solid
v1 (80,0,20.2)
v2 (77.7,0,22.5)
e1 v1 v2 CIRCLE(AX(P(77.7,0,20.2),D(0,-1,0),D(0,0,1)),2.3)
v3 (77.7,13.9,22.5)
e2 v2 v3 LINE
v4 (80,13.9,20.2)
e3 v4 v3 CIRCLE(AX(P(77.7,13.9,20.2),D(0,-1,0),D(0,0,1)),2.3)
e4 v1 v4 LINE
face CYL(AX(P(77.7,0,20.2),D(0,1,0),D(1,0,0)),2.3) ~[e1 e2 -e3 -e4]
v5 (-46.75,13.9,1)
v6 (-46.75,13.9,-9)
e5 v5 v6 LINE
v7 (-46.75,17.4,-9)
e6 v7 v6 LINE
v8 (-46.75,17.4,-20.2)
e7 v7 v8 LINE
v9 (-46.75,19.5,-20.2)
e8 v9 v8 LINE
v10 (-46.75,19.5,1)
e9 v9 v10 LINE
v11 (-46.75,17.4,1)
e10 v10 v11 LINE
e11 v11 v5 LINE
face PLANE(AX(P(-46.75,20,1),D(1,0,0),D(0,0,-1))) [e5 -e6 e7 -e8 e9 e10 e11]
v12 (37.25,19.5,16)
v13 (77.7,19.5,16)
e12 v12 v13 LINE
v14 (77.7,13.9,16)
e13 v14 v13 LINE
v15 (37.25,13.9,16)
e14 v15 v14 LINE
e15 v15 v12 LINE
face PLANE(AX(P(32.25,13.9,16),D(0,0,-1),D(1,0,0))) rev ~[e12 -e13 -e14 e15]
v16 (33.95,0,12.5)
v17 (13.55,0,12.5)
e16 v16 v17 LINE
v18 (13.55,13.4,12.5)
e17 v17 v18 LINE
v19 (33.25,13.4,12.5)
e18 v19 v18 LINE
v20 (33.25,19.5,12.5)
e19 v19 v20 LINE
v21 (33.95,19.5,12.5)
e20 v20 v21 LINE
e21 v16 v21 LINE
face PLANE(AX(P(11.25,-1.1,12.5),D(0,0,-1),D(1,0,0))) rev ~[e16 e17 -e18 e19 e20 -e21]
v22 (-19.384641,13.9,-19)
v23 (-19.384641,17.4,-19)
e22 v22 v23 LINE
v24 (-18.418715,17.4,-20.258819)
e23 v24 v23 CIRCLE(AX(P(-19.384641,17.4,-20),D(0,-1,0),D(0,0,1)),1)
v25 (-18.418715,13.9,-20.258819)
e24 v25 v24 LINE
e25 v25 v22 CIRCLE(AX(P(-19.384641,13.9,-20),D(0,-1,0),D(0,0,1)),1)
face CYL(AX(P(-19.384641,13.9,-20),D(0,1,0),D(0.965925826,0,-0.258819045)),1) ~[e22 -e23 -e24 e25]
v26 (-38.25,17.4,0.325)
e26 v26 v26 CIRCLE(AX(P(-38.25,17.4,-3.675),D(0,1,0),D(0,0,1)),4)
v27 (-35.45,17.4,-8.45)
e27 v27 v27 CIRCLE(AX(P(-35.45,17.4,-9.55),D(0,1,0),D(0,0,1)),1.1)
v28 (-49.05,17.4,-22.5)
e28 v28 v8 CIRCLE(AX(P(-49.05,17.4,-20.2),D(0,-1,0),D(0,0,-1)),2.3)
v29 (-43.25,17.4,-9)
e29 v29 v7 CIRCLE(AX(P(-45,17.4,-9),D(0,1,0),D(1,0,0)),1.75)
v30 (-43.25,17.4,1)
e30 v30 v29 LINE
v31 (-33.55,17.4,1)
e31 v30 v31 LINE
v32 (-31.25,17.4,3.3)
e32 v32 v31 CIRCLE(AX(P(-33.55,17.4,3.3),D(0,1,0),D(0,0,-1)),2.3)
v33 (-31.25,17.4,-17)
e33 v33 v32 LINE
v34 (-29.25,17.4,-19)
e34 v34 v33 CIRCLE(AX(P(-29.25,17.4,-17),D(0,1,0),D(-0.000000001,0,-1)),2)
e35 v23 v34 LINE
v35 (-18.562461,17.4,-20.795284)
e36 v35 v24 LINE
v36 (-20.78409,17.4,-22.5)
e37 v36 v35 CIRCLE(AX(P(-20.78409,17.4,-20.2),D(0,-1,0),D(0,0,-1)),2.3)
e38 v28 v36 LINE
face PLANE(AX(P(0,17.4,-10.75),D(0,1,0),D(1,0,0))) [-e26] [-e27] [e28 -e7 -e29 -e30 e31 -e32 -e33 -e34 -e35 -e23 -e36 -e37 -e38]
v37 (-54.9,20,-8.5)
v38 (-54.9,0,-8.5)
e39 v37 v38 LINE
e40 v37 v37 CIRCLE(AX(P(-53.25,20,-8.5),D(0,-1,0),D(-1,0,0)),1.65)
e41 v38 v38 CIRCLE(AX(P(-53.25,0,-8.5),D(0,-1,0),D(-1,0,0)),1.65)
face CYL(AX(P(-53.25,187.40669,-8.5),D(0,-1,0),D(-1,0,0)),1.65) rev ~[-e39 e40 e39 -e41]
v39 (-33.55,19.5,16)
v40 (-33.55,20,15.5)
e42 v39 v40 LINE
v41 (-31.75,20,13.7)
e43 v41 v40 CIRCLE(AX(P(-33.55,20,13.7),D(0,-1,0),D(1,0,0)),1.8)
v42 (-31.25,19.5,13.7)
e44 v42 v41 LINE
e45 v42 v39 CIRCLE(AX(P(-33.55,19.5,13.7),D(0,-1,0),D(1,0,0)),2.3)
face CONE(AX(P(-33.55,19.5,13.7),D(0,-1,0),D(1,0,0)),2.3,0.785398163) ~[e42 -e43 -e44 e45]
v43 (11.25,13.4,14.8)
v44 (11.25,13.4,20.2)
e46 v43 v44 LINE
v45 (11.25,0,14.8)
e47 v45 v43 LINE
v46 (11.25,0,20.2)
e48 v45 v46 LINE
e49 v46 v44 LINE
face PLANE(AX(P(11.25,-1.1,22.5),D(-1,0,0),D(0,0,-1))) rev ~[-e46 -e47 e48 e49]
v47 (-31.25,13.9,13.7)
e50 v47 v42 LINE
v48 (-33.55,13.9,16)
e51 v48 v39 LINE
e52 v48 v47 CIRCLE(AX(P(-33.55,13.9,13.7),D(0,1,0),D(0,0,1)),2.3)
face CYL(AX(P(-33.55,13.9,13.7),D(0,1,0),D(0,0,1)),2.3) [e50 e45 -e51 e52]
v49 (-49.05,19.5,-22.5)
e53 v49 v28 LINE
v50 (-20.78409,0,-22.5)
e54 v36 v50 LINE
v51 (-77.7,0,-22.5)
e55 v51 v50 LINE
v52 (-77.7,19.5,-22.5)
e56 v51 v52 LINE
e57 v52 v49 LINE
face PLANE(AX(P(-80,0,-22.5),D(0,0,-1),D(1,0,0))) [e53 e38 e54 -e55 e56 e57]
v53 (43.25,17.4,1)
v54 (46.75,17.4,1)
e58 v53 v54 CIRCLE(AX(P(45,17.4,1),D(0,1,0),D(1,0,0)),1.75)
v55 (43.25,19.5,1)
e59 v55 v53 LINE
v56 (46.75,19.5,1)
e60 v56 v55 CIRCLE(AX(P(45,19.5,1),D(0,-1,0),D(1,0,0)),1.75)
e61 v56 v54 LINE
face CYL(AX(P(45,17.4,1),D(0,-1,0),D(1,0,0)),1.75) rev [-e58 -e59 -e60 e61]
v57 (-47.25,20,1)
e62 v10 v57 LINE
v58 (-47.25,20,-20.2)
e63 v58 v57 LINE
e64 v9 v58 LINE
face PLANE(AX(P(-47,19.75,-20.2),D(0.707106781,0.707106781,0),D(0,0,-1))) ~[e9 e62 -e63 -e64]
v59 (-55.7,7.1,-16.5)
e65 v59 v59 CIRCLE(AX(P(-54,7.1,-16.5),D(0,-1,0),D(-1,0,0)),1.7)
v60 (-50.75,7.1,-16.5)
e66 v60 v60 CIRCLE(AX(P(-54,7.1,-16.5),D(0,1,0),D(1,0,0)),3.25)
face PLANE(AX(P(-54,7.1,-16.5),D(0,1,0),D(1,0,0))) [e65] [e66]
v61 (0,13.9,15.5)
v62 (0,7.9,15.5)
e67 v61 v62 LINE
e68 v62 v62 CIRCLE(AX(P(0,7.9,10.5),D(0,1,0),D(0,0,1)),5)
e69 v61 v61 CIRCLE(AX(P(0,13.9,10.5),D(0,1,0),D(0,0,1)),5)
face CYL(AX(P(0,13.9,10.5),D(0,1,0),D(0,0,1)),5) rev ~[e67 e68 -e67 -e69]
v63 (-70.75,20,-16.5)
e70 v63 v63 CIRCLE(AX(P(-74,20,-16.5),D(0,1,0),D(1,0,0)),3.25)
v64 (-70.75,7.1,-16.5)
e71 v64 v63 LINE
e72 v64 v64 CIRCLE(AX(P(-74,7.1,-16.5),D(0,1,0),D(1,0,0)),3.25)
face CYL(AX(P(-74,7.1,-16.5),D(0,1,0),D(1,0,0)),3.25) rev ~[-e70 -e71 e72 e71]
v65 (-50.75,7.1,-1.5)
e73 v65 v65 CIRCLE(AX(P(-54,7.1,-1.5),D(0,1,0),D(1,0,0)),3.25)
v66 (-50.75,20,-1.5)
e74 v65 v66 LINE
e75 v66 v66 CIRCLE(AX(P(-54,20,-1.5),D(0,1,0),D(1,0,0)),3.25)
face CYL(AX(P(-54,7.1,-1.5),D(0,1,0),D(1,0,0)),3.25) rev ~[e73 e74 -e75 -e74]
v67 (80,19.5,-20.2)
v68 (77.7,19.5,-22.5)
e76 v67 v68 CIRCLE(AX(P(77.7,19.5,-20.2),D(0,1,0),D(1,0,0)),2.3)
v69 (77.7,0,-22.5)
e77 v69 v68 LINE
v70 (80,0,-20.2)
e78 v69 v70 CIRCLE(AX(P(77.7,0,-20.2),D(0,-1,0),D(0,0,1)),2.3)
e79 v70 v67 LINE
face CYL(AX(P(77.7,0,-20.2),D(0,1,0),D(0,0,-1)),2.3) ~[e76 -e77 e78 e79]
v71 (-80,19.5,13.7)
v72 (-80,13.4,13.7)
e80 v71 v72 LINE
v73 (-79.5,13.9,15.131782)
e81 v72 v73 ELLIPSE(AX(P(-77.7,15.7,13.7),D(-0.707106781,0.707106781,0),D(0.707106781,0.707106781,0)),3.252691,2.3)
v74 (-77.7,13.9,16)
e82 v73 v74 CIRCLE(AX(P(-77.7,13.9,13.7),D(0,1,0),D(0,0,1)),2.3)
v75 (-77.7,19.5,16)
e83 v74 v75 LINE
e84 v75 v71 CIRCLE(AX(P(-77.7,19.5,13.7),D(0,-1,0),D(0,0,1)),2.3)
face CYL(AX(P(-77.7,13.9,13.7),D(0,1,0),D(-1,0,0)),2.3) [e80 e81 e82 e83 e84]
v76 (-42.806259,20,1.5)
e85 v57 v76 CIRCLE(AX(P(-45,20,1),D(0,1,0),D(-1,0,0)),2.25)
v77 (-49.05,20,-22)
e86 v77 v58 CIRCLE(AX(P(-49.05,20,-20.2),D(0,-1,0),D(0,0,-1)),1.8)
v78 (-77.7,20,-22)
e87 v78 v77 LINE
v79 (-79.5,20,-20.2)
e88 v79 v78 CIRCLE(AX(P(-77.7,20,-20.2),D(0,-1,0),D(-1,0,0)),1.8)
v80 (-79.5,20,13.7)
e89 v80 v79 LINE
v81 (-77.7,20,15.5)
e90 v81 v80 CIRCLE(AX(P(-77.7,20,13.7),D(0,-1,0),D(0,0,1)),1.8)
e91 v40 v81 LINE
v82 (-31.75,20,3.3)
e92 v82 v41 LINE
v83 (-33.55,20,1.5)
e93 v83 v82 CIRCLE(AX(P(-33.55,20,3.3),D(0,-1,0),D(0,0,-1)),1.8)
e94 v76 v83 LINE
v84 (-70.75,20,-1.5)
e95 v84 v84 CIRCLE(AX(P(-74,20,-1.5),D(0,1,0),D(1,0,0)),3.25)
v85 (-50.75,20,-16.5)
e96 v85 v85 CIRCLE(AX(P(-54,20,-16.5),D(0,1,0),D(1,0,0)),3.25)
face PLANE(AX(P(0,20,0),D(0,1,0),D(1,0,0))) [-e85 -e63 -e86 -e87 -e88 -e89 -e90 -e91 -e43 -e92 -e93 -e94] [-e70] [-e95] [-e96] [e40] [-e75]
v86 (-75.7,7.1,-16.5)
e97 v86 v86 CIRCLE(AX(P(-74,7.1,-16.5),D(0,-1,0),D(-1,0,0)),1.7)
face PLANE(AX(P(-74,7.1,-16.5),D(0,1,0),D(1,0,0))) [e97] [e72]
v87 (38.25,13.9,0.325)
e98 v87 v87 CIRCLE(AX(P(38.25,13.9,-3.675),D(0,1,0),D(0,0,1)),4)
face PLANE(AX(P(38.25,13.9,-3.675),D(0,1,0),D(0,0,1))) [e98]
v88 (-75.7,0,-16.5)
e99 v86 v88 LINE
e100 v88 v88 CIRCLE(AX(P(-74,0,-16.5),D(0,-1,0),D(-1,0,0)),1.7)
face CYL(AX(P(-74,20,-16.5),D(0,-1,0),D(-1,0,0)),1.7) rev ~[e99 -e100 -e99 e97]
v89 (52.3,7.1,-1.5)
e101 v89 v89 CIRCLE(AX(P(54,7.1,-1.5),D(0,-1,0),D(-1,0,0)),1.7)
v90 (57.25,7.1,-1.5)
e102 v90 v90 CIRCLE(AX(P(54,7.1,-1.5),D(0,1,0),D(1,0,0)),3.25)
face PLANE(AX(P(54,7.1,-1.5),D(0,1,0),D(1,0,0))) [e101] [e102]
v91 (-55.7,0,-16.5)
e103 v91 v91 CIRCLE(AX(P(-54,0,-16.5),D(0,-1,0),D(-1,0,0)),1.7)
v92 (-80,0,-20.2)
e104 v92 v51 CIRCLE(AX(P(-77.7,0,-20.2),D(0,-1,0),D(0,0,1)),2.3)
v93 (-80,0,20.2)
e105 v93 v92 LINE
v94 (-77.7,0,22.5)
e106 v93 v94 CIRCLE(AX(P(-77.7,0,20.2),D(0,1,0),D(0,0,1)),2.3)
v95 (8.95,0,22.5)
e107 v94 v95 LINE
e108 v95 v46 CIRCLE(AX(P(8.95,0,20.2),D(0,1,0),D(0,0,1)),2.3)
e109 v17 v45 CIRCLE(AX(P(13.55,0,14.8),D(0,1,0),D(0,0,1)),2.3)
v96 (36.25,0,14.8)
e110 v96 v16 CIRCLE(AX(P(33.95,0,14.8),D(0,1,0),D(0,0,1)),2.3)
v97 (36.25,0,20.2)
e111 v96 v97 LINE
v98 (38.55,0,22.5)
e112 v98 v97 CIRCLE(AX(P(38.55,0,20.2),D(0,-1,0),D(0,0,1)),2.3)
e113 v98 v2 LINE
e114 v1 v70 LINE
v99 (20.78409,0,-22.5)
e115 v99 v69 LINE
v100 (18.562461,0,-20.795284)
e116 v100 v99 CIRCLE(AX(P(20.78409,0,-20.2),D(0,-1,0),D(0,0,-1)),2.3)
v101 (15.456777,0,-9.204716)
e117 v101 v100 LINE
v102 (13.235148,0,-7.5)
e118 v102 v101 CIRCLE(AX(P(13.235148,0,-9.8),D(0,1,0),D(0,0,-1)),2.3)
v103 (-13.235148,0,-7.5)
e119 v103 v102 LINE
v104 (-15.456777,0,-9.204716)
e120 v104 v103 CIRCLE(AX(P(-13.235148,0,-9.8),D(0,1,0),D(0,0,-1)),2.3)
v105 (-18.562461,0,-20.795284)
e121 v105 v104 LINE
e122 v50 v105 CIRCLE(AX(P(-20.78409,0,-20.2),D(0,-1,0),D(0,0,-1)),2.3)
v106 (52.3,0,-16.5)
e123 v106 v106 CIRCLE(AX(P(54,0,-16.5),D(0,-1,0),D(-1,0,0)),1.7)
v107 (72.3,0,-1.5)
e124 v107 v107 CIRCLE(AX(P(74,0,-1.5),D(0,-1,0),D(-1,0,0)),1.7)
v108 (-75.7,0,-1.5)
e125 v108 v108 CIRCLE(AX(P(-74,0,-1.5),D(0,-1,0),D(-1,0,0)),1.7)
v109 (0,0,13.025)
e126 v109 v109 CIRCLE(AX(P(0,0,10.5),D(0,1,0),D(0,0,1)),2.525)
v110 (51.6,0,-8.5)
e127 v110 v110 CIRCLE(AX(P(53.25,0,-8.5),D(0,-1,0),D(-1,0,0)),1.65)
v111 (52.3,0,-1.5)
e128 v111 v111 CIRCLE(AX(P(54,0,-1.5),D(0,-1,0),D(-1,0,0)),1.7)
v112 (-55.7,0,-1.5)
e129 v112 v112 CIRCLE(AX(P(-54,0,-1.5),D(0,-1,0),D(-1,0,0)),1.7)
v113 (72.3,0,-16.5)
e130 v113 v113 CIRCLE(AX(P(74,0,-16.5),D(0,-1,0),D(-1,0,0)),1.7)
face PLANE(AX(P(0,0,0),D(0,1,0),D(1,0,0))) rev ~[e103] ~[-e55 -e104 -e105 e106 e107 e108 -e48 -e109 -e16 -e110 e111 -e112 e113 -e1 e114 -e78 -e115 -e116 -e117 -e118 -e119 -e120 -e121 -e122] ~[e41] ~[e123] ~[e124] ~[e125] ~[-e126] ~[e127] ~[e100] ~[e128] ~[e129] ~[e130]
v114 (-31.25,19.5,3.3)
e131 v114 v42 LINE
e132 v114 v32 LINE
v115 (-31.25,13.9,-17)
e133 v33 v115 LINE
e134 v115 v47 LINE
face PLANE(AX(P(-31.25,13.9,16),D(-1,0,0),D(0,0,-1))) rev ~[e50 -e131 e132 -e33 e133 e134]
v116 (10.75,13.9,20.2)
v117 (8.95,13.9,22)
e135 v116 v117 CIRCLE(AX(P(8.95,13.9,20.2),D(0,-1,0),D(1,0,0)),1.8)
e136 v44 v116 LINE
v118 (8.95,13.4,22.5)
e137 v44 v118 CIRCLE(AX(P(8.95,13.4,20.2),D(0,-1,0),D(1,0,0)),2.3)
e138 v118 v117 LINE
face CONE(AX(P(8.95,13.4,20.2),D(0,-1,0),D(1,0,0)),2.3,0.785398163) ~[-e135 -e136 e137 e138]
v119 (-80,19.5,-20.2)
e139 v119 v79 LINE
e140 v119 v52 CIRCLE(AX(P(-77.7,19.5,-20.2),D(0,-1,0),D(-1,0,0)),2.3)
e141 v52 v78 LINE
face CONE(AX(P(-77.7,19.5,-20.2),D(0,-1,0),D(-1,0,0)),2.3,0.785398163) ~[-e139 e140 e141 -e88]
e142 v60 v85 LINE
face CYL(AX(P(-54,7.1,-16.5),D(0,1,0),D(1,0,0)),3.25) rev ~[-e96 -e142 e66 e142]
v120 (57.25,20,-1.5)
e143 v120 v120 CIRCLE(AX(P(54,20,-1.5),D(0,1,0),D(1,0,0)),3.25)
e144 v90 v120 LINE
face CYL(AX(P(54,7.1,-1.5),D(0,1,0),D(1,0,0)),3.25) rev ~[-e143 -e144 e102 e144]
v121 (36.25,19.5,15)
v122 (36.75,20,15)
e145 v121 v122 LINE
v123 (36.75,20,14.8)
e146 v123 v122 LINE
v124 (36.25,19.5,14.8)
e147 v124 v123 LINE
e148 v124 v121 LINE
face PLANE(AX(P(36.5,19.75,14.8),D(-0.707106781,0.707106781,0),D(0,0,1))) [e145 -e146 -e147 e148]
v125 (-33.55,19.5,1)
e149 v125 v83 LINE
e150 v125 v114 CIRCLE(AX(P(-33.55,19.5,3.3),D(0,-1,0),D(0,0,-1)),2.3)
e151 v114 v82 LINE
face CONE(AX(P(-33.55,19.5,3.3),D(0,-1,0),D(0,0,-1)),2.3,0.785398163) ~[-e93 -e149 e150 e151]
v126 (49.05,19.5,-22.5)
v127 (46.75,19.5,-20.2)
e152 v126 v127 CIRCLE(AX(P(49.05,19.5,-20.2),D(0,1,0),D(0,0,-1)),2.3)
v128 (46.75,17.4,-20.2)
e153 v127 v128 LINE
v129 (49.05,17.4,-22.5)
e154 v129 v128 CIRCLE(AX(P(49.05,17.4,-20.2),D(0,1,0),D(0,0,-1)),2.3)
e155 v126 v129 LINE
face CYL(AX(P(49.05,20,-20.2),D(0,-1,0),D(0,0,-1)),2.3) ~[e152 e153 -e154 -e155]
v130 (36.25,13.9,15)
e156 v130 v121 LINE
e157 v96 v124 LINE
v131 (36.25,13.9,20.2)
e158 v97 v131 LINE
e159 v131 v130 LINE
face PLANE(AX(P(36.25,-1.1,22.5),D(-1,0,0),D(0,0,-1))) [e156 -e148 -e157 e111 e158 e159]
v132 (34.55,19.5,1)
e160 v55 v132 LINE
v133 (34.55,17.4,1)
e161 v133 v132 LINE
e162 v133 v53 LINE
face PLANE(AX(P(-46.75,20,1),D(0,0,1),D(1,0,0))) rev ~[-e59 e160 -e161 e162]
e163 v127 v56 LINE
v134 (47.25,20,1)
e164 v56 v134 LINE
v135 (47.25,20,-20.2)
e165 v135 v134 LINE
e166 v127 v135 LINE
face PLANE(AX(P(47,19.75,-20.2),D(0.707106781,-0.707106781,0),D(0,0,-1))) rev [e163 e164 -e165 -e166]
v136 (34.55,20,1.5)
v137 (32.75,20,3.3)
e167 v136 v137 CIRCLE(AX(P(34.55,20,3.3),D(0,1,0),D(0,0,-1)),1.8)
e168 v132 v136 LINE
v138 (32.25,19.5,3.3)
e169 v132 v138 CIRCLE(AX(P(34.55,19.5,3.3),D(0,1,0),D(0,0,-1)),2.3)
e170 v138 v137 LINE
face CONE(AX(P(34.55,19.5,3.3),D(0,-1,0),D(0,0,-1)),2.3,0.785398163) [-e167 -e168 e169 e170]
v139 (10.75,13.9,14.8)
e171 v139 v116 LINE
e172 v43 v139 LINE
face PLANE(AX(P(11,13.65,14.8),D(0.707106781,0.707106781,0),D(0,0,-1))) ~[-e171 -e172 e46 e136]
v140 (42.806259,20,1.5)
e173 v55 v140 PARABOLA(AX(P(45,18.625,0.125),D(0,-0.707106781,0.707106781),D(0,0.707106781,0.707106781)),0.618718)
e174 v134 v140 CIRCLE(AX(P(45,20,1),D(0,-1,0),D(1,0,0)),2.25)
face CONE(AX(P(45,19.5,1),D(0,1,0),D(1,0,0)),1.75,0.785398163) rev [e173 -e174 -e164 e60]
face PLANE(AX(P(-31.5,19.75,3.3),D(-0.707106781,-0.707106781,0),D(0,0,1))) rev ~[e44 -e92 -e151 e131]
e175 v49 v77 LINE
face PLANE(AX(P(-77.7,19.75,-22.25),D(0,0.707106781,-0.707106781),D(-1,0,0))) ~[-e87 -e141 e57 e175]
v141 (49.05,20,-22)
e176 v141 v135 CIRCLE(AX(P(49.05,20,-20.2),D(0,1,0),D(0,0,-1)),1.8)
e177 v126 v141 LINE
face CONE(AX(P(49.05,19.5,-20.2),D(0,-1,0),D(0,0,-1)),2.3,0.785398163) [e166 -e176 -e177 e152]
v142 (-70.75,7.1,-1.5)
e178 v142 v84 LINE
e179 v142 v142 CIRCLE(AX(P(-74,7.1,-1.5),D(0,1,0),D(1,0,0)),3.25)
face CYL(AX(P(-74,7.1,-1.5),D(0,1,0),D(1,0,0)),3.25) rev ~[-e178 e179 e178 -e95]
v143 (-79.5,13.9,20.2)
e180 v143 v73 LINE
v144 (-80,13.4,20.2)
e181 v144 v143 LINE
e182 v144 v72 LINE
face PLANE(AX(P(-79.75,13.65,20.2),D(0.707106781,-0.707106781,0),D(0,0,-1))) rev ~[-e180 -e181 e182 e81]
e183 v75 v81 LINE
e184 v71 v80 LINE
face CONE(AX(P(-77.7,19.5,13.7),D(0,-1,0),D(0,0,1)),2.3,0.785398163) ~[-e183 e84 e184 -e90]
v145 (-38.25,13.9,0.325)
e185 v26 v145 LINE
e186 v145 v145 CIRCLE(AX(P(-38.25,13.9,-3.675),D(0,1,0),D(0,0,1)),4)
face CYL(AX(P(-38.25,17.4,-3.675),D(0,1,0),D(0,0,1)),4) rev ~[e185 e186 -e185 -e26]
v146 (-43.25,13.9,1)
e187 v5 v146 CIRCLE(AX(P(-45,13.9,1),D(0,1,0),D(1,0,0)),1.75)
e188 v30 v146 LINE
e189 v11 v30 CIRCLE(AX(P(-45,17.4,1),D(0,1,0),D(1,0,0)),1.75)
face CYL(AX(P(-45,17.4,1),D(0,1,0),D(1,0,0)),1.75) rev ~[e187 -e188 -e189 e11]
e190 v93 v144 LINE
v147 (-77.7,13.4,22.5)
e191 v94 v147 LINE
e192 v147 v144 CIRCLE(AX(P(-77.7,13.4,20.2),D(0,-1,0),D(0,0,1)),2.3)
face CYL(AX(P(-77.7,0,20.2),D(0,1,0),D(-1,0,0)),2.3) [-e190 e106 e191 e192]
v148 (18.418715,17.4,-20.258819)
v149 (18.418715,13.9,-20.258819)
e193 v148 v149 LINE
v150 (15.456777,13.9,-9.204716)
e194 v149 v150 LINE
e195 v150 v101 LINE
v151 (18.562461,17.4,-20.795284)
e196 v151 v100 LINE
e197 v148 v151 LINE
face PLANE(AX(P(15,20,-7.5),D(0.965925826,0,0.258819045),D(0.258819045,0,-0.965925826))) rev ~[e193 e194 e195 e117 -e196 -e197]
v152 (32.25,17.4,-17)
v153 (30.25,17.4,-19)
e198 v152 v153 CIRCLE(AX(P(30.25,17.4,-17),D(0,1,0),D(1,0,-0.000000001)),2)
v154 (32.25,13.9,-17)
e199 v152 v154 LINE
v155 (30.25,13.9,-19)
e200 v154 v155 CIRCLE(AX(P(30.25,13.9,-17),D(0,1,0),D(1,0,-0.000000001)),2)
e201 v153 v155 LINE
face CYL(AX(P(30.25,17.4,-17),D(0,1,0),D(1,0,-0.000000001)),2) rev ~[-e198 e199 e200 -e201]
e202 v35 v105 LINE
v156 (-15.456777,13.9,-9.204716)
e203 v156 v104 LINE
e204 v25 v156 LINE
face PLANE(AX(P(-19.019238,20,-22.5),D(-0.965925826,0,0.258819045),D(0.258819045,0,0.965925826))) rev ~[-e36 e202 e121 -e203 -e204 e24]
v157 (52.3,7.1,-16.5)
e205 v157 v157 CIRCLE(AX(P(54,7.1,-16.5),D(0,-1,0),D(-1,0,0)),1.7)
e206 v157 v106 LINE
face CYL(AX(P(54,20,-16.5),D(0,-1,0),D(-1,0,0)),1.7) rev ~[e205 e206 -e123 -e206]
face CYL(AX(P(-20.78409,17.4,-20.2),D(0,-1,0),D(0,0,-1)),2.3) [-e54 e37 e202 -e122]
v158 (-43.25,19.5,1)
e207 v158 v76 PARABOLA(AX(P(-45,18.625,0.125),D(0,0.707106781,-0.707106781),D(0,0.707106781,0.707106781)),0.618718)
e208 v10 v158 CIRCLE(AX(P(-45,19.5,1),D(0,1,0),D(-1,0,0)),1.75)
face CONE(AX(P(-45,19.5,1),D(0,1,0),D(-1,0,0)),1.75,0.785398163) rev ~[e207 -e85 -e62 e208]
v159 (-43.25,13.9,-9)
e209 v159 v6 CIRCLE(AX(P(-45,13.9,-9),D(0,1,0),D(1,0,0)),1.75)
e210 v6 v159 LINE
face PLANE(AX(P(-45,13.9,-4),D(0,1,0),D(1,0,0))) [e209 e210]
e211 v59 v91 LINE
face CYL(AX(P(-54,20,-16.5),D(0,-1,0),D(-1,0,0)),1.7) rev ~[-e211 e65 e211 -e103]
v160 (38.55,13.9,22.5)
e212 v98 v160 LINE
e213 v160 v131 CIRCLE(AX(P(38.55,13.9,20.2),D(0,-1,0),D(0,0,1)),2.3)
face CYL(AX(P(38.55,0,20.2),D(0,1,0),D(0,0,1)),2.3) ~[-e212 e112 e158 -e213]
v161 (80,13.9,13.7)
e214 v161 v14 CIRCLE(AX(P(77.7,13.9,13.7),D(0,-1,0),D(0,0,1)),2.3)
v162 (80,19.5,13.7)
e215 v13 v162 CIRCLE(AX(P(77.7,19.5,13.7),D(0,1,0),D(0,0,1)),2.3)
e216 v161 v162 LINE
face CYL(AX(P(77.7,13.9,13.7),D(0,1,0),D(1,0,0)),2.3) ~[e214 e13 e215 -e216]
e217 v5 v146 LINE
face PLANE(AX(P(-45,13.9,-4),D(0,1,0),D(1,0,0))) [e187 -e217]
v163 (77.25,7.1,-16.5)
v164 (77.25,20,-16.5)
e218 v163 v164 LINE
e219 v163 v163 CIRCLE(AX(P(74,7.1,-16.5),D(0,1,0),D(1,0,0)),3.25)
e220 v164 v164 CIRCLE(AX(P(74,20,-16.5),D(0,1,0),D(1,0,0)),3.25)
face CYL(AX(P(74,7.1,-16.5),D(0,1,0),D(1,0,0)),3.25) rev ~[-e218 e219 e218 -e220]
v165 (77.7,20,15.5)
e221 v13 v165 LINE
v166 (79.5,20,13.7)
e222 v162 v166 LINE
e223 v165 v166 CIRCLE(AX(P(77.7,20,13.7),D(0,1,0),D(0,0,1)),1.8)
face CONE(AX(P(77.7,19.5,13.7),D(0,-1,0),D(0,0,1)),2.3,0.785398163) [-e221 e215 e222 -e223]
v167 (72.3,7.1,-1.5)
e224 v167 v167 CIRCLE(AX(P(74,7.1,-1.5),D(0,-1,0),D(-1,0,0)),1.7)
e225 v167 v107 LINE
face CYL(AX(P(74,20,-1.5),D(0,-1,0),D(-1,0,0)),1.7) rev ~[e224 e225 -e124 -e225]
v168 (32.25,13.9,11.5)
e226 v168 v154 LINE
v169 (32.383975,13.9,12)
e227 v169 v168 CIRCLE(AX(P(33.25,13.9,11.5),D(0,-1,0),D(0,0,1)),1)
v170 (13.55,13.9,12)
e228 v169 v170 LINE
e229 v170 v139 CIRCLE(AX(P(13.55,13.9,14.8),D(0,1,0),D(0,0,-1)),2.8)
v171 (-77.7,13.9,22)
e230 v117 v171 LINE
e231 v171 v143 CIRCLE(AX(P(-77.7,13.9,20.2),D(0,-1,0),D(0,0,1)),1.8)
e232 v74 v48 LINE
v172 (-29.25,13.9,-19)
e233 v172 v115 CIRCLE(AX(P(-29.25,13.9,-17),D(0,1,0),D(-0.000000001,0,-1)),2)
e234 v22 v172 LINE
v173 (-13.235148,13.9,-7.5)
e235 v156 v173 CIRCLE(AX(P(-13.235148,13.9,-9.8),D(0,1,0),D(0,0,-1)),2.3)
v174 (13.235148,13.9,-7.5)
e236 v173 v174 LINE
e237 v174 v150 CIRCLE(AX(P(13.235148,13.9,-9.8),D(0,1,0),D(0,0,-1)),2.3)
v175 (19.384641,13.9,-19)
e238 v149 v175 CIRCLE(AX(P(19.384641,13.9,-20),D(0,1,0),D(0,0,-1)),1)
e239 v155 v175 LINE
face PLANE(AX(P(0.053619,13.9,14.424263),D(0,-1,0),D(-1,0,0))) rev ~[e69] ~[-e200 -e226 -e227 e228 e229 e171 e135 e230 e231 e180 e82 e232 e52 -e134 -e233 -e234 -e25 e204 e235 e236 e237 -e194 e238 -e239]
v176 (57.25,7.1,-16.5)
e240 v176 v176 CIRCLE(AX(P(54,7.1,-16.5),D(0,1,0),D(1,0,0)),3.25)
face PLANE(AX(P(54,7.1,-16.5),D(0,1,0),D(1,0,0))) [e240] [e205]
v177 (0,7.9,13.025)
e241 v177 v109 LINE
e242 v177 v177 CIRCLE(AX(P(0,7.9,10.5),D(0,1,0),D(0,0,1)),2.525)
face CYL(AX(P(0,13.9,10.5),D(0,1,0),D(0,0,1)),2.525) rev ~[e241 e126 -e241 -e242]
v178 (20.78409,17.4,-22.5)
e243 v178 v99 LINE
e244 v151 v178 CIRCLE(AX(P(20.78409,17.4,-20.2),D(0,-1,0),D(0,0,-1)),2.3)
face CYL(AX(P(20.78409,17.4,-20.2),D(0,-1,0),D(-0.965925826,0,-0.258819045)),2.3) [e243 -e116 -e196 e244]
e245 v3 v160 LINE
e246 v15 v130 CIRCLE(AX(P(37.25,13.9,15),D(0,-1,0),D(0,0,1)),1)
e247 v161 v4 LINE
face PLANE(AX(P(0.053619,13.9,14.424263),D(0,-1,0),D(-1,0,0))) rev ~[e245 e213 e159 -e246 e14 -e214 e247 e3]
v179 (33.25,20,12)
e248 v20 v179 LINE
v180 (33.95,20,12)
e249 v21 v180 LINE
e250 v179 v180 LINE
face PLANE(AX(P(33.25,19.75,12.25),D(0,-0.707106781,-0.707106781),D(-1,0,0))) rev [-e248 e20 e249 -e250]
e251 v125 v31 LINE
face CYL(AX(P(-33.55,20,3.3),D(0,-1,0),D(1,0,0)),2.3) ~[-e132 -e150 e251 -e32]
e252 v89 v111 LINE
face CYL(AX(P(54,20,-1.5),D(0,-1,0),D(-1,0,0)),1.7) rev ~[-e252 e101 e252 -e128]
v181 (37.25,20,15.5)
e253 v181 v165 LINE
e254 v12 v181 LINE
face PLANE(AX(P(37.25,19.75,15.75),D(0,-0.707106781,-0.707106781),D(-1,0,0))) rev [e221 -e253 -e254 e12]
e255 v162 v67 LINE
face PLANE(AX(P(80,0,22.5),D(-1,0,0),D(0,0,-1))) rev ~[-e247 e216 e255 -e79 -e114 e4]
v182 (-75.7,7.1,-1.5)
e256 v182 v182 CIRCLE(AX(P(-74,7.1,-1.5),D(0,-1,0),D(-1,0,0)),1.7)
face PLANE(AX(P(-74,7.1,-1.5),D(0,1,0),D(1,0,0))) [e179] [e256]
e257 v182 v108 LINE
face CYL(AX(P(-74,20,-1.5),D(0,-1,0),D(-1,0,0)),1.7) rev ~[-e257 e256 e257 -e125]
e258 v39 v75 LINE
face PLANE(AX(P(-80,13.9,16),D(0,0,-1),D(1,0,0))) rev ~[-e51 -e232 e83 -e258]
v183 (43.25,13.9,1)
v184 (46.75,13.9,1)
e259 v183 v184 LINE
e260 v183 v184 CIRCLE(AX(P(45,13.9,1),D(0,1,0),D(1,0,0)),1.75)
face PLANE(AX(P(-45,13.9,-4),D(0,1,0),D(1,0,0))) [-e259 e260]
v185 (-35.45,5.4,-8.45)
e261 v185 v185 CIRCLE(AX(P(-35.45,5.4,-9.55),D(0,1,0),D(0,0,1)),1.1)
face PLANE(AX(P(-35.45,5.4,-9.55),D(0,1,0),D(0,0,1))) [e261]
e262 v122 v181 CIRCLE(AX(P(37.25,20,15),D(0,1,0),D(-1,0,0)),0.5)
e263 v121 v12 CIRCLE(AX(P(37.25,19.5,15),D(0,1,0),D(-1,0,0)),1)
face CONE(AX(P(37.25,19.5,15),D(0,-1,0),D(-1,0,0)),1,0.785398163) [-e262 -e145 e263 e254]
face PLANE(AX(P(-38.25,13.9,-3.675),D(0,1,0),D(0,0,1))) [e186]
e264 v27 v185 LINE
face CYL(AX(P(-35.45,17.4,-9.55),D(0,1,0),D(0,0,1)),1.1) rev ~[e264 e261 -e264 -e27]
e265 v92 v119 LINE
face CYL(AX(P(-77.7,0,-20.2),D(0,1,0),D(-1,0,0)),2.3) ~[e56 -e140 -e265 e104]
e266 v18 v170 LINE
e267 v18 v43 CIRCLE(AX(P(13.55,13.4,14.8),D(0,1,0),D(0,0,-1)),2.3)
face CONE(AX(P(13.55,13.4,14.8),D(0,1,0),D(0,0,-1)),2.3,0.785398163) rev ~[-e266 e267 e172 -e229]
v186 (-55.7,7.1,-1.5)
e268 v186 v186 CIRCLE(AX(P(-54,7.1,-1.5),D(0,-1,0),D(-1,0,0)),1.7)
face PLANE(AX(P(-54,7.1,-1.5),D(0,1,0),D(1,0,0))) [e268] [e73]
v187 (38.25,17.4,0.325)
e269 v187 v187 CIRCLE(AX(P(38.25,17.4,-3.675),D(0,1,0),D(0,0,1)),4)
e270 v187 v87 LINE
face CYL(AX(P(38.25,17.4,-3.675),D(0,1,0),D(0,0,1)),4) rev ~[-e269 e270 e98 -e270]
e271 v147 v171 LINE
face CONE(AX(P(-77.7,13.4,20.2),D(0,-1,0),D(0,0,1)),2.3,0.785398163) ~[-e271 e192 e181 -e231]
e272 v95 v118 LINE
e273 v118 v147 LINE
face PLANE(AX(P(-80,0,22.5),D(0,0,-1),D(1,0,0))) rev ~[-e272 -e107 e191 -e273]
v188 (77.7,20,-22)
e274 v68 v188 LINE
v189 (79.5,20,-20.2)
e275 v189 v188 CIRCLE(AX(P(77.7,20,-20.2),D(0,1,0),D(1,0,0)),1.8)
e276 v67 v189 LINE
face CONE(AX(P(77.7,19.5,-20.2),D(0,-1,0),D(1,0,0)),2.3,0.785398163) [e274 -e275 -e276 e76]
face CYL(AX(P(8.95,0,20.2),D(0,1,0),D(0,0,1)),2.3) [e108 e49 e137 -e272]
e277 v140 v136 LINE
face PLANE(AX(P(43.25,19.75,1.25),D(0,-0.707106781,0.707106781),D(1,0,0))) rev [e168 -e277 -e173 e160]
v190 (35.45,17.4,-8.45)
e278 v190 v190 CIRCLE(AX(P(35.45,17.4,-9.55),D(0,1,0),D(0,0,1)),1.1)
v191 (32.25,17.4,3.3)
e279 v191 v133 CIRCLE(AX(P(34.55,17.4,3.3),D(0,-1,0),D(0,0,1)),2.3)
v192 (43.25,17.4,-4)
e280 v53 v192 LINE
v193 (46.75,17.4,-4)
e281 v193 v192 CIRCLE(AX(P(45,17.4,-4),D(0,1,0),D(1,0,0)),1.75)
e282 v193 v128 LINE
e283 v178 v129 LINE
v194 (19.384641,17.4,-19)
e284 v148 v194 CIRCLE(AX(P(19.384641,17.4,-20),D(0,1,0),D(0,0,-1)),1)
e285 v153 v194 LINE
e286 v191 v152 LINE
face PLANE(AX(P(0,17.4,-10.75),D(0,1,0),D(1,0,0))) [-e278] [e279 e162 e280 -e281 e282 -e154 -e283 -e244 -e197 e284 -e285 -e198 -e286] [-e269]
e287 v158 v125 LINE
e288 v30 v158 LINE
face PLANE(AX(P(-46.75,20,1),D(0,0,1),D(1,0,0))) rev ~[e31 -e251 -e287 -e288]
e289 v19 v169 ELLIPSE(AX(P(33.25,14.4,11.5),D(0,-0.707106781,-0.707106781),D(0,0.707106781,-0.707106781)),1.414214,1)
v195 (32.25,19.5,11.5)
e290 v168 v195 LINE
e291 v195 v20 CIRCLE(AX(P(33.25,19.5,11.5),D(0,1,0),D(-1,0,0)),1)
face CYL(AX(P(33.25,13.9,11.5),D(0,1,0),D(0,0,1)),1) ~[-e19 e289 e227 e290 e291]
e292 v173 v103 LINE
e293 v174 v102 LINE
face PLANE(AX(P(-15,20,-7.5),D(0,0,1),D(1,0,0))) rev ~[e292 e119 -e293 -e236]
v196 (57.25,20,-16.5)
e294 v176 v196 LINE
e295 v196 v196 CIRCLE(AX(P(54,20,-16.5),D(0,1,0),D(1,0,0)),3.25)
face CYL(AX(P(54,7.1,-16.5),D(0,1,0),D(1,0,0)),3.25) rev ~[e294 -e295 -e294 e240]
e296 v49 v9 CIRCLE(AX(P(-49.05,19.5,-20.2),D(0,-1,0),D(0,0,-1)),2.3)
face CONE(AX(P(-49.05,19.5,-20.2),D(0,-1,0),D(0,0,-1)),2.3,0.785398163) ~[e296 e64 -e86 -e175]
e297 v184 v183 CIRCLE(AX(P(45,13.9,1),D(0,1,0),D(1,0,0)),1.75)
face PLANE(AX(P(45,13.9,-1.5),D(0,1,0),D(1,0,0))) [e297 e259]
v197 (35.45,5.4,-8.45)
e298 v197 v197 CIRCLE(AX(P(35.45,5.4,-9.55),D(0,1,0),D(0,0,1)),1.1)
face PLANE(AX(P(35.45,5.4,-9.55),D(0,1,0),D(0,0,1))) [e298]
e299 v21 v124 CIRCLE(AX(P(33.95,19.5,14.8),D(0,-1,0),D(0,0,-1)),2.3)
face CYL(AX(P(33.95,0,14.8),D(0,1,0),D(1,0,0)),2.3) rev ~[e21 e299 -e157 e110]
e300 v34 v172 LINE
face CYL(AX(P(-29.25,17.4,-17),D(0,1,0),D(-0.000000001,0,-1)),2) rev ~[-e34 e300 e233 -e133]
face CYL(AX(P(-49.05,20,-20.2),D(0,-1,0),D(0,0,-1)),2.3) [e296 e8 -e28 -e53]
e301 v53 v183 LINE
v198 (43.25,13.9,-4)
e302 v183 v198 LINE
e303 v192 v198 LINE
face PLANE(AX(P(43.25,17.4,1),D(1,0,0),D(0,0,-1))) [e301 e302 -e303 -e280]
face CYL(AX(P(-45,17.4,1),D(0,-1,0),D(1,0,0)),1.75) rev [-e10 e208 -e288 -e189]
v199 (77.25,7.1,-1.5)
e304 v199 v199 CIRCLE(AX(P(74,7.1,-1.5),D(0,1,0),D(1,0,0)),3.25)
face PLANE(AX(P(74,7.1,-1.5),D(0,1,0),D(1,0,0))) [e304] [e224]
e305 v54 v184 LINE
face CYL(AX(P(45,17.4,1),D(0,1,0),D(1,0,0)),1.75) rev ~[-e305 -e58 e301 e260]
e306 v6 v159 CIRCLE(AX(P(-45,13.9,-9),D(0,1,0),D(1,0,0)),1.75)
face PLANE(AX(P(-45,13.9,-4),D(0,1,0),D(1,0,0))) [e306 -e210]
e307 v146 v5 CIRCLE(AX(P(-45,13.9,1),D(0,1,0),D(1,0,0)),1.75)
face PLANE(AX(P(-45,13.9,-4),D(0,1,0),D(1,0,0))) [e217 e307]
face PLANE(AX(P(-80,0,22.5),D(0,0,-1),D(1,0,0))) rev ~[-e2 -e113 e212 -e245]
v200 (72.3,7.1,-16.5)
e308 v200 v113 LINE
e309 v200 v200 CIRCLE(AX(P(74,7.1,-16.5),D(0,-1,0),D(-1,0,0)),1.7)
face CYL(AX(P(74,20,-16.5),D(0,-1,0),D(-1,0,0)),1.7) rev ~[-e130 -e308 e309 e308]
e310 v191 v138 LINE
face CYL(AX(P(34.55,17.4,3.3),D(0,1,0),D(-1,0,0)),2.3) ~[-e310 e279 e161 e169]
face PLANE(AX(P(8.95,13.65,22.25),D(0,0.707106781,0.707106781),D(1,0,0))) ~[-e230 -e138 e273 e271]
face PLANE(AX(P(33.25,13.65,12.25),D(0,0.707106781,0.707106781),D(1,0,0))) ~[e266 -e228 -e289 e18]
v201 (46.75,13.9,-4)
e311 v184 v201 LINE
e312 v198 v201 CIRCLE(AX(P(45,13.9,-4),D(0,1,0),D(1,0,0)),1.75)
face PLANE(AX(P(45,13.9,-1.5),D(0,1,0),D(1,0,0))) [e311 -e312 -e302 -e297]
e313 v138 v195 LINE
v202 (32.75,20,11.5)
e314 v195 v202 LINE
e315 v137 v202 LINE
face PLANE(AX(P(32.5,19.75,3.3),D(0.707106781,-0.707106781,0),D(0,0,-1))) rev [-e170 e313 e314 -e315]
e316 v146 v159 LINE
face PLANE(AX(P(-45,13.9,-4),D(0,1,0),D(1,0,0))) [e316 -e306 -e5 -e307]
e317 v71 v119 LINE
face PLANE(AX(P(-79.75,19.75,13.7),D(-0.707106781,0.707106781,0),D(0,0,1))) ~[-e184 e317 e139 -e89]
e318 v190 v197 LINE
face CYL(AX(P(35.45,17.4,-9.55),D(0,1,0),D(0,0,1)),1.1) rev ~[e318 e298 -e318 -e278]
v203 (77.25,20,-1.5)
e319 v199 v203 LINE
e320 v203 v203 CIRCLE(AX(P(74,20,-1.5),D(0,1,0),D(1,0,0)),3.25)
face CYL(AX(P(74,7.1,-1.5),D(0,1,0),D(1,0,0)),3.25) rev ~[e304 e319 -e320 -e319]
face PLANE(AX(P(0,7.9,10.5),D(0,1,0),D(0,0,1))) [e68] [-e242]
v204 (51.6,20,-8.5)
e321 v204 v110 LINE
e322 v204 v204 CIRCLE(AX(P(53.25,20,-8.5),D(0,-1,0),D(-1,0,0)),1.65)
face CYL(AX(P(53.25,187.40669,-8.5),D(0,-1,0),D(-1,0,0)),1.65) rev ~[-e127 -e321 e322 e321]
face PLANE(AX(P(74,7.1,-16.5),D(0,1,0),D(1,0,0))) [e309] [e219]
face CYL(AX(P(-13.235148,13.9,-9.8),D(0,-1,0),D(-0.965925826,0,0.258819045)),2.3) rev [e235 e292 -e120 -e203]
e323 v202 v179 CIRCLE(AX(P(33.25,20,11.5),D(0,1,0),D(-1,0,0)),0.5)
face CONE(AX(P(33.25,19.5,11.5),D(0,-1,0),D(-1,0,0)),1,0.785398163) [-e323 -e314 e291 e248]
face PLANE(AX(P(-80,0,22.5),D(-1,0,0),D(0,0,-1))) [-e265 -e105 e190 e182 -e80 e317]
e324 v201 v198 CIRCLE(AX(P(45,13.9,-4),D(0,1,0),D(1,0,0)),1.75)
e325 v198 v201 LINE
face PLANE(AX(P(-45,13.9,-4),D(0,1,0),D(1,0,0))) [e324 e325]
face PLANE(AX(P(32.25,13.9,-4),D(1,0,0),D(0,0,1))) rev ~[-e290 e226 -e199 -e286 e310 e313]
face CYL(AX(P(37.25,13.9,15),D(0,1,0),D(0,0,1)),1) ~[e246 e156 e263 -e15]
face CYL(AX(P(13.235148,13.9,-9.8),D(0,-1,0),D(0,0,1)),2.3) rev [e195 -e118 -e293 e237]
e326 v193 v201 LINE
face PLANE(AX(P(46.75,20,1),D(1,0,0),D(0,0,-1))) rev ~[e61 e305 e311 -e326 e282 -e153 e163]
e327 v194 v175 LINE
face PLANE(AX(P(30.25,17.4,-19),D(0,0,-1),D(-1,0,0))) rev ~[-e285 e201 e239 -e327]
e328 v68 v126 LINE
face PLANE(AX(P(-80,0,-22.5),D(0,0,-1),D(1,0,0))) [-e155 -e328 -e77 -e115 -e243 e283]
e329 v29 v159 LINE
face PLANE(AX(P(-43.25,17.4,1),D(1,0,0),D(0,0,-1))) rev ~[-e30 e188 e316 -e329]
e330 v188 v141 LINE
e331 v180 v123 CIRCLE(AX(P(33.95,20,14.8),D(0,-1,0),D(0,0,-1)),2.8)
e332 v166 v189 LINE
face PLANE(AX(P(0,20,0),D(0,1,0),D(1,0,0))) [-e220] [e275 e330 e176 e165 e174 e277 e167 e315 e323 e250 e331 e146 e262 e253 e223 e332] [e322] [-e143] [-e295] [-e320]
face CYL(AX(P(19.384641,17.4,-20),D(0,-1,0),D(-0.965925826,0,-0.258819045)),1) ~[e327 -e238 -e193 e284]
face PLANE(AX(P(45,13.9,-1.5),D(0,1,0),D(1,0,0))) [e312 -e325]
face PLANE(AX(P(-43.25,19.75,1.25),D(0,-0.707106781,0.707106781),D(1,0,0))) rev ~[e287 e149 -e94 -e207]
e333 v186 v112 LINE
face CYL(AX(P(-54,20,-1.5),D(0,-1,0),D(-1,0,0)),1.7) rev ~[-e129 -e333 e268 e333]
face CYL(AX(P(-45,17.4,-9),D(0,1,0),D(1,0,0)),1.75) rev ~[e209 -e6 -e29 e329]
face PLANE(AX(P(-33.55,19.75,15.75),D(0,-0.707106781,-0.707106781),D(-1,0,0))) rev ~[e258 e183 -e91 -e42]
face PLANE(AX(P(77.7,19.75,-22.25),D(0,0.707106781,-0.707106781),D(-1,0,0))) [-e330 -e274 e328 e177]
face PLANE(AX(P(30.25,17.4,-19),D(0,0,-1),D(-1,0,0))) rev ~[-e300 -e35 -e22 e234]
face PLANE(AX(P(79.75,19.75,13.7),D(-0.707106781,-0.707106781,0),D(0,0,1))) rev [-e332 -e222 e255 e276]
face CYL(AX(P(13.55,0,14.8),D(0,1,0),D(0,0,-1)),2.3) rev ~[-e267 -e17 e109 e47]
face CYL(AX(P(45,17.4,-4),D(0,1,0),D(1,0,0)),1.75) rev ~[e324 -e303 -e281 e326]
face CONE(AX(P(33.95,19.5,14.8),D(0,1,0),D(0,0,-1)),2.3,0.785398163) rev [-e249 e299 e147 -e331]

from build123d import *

# Parameters (mm, degrees)
SKETCH1_W                                           = 160
SKETCH1_H                                           = 45
BOSS_EXTRUDE1_DEPTH                                 = 20
SKETCH2_W                                           = 93.5
SKETCH2_H                                           = 23.5
CUT_EXTRUDE1_DEPTH                                  = 2.6
CUT_EXTRUDE14_DEPTH                                 = 3.5
CUT_EXTRUDE7_DEPTH                                  = 86.476604986
SKETCH24_R                                          = 4
SKETCH24_W                                          = 3.5
SKETCH24_H                                          = 10
SKETCH24_H_2                                        = 5
CUT_EXTRUDE16_DEPTH                                 = 3.5
CUT_EXTRUDE17_DEPTH                                 = 10
SKETCH23_R                                          = 1.75
CUT_EXTRUDE15_DEPTH                                 = 10
CUT_EXTRUDE15_DIRECTION_2_REACH                     = 86.906
SKETCH26_R                                          = 1.1
CUT_EXTRUDE18_DEPTH                                 = 12
CBORE_FOR_M3_HEX_SOCKET_HEAD_CAP_SCREW1_D           = 3.4
CBORE_FOR_M3_HEX_SOCKET_HEAD_CAP_SCREW1_CBORE_D     = 6.5
CBORE_FOR_M3_HEX_SOCKET_HEAD_CAP_SCREW1_CBORE_DEPTH = 12.9
SKETCH32_R                                          = 2.525
CUT_EXTRUDE19_DEPTH                                 = 30
M4_TAPPED_HOLE1_D                                   = 3.3
SKETCH35_R                                          = 5
CUT_EXTRUDE20_DEPTH                                 = 6
CUT_EXTRUDE21_DEPTH                                 = 10
CUT_EXTRUDE21_DEPTH_BACK                            = 15
SKETCH36_W                                          = 25
SKETCH36_H                                          = 10
FILLET1_R                                           = 2.3
FILLET2_R                                           = 1
CHAMFER1_SIZE                                       = 0.5


with BuildPart() as part:
    # Sketch1 → Boss-Extrude1 (new body)
    with BuildSketch(Plane(origin=(0, 0, 0), x_dir=(1, 0, 0), z_dir=(0, 1, 0))):
        Rectangle(SKETCH1_W, SKETCH1_H)
    extrude(amount=BOSS_EXTRUDE1_DEPTH)

    # Sketch2 → Cut-Extrude1 (cut)
    with BuildSketch(Plane(origin=(0, 20, 0), x_dir=(1, 0, 0), z_dir=(0, 1, 0))):
        with Locations((0, 10.75)):
            Rectangle(SKETCH2_W, SKETCH2_H)
    extrude(amount=-CUT_EXTRUDE1_DEPTH, mode=Mode.SUBTRACT)

    # Sketch9 → Cut-Extrude14 (cut)
    with BuildSketch(Plane(origin=(0, 17.4, 0), x_dir=(1, 0, 0), z_dir=(0, 1, 0))):
        with BuildLine():
            Line((-29.25, -1), (30.25, -1))
            ThreePointArc((30.25, -1), (31.664213562, -0.414213562), (32.25, 1))
            Line((32.25, 1), (32.25, 17))
            ThreePointArc((32.25, 17), (31.664213562, 18.414213562), (30.25, 19))
            Line((30.25, 19), (-29.25, 19))
            ThreePointArc((-29.25, 19), (-30.664213562, 18.414213562), (-31.25, 17))
            Line((-31.25, 17), (-31.25, 1))
            ThreePointArc((-31.25, 1), (-30.664213562, -0.414213562), (-29.25, -1))
        make_face()
    extrude(amount=-CUT_EXTRUDE14_DEPTH, mode=Mode.SUBTRACT)

    # Sketch12 → Cut-Extrude7 (cut, through all)
    with BuildSketch(Plane(origin=(0, 20, 0), x_dir=(1, 0, 0), z_dir=(0, 1, 0))):
        Polygon((-19.019237886, 22.5), (-15, 7.5), (15, 7.5), (19.019237886, 22.5), align=None)
    extrude(amount=-CUT_EXTRUDE7_DEPTH, mode=Mode.SUBTRACT)

    # Sketch24 → Cut-Extrude16 (cut)
    with BuildSketch(Plane(origin=(0, 17.4, 0), x_dir=(1, 0, 0), z_dir=(0, 1, 0))):
        with Locations(Location((-38.25, 3.675, 0), (0, 0, 270))):
            Circle(SKETCH24_R)
        with Locations(Location((38.25, 3.675, 0), (0, 0, 270))):
            Circle(SKETCH24_R)
        with Locations((-45, 4)):
            Rectangle(SKETCH24_W, SKETCH24_H)
        with Locations((45, 1.5)):
            Rectangle(SKETCH24_W, SKETCH24_H_2)
    extrude(amount=-CUT_EXTRUDE16_DEPTH, mode=Mode.SUBTRACT)

    # Sketch25 → Cut-Extrude17 (cut)
    with BuildSketch(Plane(origin=(0, 13.9, 0), x_dir=(1, 0, 0), z_dir=(0, 1, 0))):
        Polygon((-31.25, 4), (32.25, 4), (32.25, -16), (80, -16), (80, -22.5), (-80, -22.5), (-80, -16), (-31.25, -16), align=None)
    extrude(amount=CUT_EXTRUDE17_DEPTH, mode=Mode.SUBTRACT)

    # Sketch23 → Cut-Extrude15 (cut)
    with BuildSketch(Plane(origin=(0, 17.4, 0), x_dir=(1, 0, 0), z_dir=(0, 1, 0))):
        with Locations((-45, -1)):
            Circle(SKETCH23_R)
        with Locations((45, -1)):
            Circle(SKETCH23_R)
        with Locations((-45, 9)):
            Circle(SKETCH23_R)
        with Locations((45, 4)):
            Circle(SKETCH23_R)
    extrude(amount=CUT_EXTRUDE15_DEPTH, mode=Mode.SUBTRACT)

    # Cut-Extrude15 direction 2: up to this face of the body (flat: up to its plane)
    cut_extrude15_direction_2_end = Plane(part.part.faces().sort_by_distance((-45, 13.9, -4))[0])
    # Sketch23 → Cut-Extrude15 direction 2 (cut, up to the picked face)
    with BuildSketch(Plane(origin=(0, 17.4, 0), x_dir=(1, 0, 0), z_dir=(0, 1, 0)), mode=Mode.PRIVATE) as cut_extrude15_direction_2_sk1:
        with Locations((-45, -1)):
            Circle(SKETCH23_R)
    cut_extrude15_direction_2_tool1 = split(extrude(cut_extrude15_direction_2_sk1.sketch, amount=-CUT_EXTRUDE15_DIRECTION_2_REACH, mode=Mode.PRIVATE), bisect_by=cut_extrude15_direction_2_end, keep=Keep.BOTH, mode=Mode.PRIVATE)
    # Sketch23 → Cut-Extrude15 direction 2 (cut, up to the picked face)
    with BuildSketch(Plane(origin=(0, 17.4, 0), x_dir=(1, 0, 0), z_dir=(0, 1, 0)), mode=Mode.PRIVATE) as cut_extrude15_direction_2_sk2:
        with Locations((45, -1)):
            Circle(SKETCH23_R)
    cut_extrude15_direction_2_tool2 = split(extrude(cut_extrude15_direction_2_sk2.sketch, amount=-CUT_EXTRUDE15_DIRECTION_2_REACH, mode=Mode.PRIVATE), bisect_by=cut_extrude15_direction_2_end, keep=Keep.BOTH, mode=Mode.PRIVATE)
    # Sketch23 → Cut-Extrude15 direction 2 (cut, up to the picked face)
    with BuildSketch(Plane(origin=(0, 17.4, 0), x_dir=(1, 0, 0), z_dir=(0, 1, 0)), mode=Mode.PRIVATE) as cut_extrude15_direction_2_sk3:
        with Locations((-45, 9)):
            Circle(SKETCH23_R)
    cut_extrude15_direction_2_tool3 = split(extrude(cut_extrude15_direction_2_sk3.sketch, amount=-CUT_EXTRUDE15_DIRECTION_2_REACH, mode=Mode.PRIVATE), bisect_by=cut_extrude15_direction_2_end, keep=Keep.BOTH, mode=Mode.PRIVATE)
    # Sketch23 → Cut-Extrude15 direction 2 (cut, up to the picked face)
    with BuildSketch(Plane(origin=(0, 17.4, 0), x_dir=(1, 0, 0), z_dir=(0, 1, 0)), mode=Mode.PRIVATE) as cut_extrude15_direction_2_sk4:
        with Locations((45, 4)):
            Circle(SKETCH23_R)
    cut_extrude15_direction_2_tool4 = split(extrude(cut_extrude15_direction_2_sk4.sketch, amount=-CUT_EXTRUDE15_DIRECTION_2_REACH, mode=Mode.PRIVATE), bisect_by=cut_extrude15_direction_2_end, keep=Keep.BOTH, mode=Mode.PRIVATE)
    add(cut_extrude15_direction_2_tool1.solids().sort_by(Axis((-45, 17.4, 1), (0, -1, 0)))[0], mode=Mode.SUBTRACT)
    add(cut_extrude15_direction_2_tool2.solids().sort_by(Axis((45, 17.4, 1), (0, -1, 0)))[0], mode=Mode.SUBTRACT)
    add(cut_extrude15_direction_2_tool3.solids().sort_by(Axis((-45, 17.4, -9), (0, -1, 0)))[0], mode=Mode.SUBTRACT)
    add(cut_extrude15_direction_2_tool4.solids().sort_by(Axis((45, 17.4, -4), (0, -1, 0)))[0], mode=Mode.SUBTRACT)

    # Sketch26 → Cut-Extrude18 (cut)
    with BuildSketch(Plane(origin=(0, 17.4, 0), x_dir=(1, 0, 0), z_dir=(0, 1, 0))):
        with Locations(Location((35.45, 9.55, 0), (0, 0, 270))):
            Circle(SKETCH26_R)
        with Locations(Location((-35.45, 9.55, 0), (0, 0, 270))):
            Circle(SKETCH26_R)
    extrude(amount=-CUT_EXTRUDE18_DEPTH, mode=Mode.SUBTRACT)

    # CBORE for M3 Hex Socket Head Cap Screw1 (through all)
    with Locations(Plane(origin=(0, 20, 0), x_dir=(1, 0, 0), z_dir=(0, 1, 0))):
        with Locations((-74, 16.5), (-74, 1.5), (-54, 1.5), (-54, 16.5), (54, 16.5), (54, 1.5), (74, 1.5), (74, 16.5)):
            CounterBoreHole(CBORE_FOR_M3_HEX_SOCKET_HEAD_CAP_SCREW1_D / 2, CBORE_FOR_M3_HEX_SOCKET_HEAD_CAP_SCREW1_CBORE_D / 2, CBORE_FOR_M3_HEX_SOCKET_HEAD_CAP_SCREW1_CBORE_DEPTH)

    # Sketch32 → Cut-Extrude19 (cut)
    with BuildSketch(Plane(origin=(0, 13.9, 0), x_dir=(1, 0, 0), z_dir=(0, 1, 0))):
        with Locations(Location((0, -10.5, 0), (0, 0, 270))):
            Circle(SKETCH32_R)
    extrude(amount=-CUT_EXTRUDE19_DEPTH, mode=Mode.SUBTRACT)

    # M4 Tapped Hole1 (through all)
    with Locations(Plane(origin=(0, 20, 0), x_dir=(1, 0, 0), z_dir=(0, 1, 0))):
        with Locations((53.25, 8.5), (-53.25, 8.5)):
            Hole(M4_TAPPED_HOLE1_D / 2)

    # Sketch35 → Cut-Extrude20 (cut)
    with BuildSketch(Plane(origin=(0, 13.9, 0), x_dir=(1, 0, 0), z_dir=(0, 1, 0))):
        with Locations(Location((0, -10.5, 0), (0, 0, 270))):
            Circle(SKETCH35_R)
    extrude(amount=-CUT_EXTRUDE20_DEPTH, mode=Mode.SUBTRACT)

    # Sketch36 → Cut-Extrude21 (cut, two sides: drawn at the far end of the back side and taken through both)
    with BuildSketch(Plane(origin=(0, 13.9, 0), x_dir=(1, 0, 0), z_dir=(0, 1, 0)).offset(-CUT_EXTRUDE21_DEPTH_BACK)):
        with Locations((23.75, -17.5)):
            Rectangle(SKETCH36_W, SKETCH36_H)
    extrude(amount=CUT_EXTRUDE21_DEPTH + CUT_EXTRUDE21_DEPTH_BACK, mode=Mode.SUBTRACT)

    # Fillet1
    fillet1_edges = [part.edges().sort_by_distance(p)[0] for p in [
        (80, 6.95, 22.5),
        (-80, 6.95, 22.5),
        (-31.25, 16.95, 16),
        (-80, 16.95, 16),
        (80, 16.95, 16),
        (-31.25, 18.7, 1),
        (32.25, 18.7, 1),
        (46.75, 18.7, -22.5),
        (-46.75, 18.7, -22.5),
        (36.25, 10, 12.5),
        (36.25, 6.95, 22.5),
        (11.25, 6.95, 12.5),
        (11.25, 6.95, 22.5),
        (-19.019237886, 8.7, -22.5),
        (19.019237886, 8.7, -22.5),
        (15, 6.95, -7.5),
        (-15, 6.95, -7.5),
        (-80, 10, -22.5),
        (80, 10, -22.5),
    ]]
    fillet(fillet1_edges, radius=FILLET1_R)

    # Fillet2
    fillet2_edges = [part.edges().sort_by_distance(p)[0] for p in [
        (36.25, 16.95, 16),
        (32.25, 16.95, 12.5),
        (18.081415713, 15.65, -19),
        (-18.081415713, 15.65, -19),
    ]]
    fillet(fillet2_edges, radius=FILLET2_R)

    # Chamfer1
    chamfer1_edges = [part.edges().sort_by_distance(p)[0] for p in [
        (-80, 13.9, 16.95),
        (-38.4, 20, 1),
        (45, 20, 2.75),
        (-45, 20, 2.75),
        (46.75, 20, -9.6),
        (38.9, 20, 1),
        (57.475, 20, 16),
        (80, 20, -3.25),
        (63.375, 20, -22.5),
        (33.6, 20, 12.5),
        (79.326345597, 20, -21.826345597),
        (79.326345597, 20, 15.326345597),
        (47.423654403, 20, -21.826345597),
        (32.923654403, 20, 1.673654403),
        (-46.75, 20, -9.6),
        (-63.375, 20, -22.5),
        (-80, 20, -3.25),
        (-55.625, 20, 16),
        (-31.25, 20, 8.5),
        (-79.326345597, 20, -21.826345597),
        (-31.923654403, 20, 15.326345597),
        (-79.326345597, 20, 15.326345597),
        (-31.923654403, 20, 1.673654403),
        (-47.423654403, 20, -21.826345597),
        (-34.375, 13.9, 22.5),
        (11.25, 13.9, 17.5),
        (23.4, 13.9, 12.5),
        (10.576345597, 13.9, 21.826345597),
        (-79.326345597, 13.9, 21.826345597),
        (11.923654403, 13.9, 13.173654403),
        (35.576345597, 20, 13.173654403),
        (32.25, 20, 7.4),
        (36.25, 20, 14.9),
        (36.542893219, 20, 15.707106781),
        (32.542893219, 20, 12.207106781),
    ]]
    chamfer(chamfer1_edges, length=CHAMFER1_SIZE)


solid = part.part
